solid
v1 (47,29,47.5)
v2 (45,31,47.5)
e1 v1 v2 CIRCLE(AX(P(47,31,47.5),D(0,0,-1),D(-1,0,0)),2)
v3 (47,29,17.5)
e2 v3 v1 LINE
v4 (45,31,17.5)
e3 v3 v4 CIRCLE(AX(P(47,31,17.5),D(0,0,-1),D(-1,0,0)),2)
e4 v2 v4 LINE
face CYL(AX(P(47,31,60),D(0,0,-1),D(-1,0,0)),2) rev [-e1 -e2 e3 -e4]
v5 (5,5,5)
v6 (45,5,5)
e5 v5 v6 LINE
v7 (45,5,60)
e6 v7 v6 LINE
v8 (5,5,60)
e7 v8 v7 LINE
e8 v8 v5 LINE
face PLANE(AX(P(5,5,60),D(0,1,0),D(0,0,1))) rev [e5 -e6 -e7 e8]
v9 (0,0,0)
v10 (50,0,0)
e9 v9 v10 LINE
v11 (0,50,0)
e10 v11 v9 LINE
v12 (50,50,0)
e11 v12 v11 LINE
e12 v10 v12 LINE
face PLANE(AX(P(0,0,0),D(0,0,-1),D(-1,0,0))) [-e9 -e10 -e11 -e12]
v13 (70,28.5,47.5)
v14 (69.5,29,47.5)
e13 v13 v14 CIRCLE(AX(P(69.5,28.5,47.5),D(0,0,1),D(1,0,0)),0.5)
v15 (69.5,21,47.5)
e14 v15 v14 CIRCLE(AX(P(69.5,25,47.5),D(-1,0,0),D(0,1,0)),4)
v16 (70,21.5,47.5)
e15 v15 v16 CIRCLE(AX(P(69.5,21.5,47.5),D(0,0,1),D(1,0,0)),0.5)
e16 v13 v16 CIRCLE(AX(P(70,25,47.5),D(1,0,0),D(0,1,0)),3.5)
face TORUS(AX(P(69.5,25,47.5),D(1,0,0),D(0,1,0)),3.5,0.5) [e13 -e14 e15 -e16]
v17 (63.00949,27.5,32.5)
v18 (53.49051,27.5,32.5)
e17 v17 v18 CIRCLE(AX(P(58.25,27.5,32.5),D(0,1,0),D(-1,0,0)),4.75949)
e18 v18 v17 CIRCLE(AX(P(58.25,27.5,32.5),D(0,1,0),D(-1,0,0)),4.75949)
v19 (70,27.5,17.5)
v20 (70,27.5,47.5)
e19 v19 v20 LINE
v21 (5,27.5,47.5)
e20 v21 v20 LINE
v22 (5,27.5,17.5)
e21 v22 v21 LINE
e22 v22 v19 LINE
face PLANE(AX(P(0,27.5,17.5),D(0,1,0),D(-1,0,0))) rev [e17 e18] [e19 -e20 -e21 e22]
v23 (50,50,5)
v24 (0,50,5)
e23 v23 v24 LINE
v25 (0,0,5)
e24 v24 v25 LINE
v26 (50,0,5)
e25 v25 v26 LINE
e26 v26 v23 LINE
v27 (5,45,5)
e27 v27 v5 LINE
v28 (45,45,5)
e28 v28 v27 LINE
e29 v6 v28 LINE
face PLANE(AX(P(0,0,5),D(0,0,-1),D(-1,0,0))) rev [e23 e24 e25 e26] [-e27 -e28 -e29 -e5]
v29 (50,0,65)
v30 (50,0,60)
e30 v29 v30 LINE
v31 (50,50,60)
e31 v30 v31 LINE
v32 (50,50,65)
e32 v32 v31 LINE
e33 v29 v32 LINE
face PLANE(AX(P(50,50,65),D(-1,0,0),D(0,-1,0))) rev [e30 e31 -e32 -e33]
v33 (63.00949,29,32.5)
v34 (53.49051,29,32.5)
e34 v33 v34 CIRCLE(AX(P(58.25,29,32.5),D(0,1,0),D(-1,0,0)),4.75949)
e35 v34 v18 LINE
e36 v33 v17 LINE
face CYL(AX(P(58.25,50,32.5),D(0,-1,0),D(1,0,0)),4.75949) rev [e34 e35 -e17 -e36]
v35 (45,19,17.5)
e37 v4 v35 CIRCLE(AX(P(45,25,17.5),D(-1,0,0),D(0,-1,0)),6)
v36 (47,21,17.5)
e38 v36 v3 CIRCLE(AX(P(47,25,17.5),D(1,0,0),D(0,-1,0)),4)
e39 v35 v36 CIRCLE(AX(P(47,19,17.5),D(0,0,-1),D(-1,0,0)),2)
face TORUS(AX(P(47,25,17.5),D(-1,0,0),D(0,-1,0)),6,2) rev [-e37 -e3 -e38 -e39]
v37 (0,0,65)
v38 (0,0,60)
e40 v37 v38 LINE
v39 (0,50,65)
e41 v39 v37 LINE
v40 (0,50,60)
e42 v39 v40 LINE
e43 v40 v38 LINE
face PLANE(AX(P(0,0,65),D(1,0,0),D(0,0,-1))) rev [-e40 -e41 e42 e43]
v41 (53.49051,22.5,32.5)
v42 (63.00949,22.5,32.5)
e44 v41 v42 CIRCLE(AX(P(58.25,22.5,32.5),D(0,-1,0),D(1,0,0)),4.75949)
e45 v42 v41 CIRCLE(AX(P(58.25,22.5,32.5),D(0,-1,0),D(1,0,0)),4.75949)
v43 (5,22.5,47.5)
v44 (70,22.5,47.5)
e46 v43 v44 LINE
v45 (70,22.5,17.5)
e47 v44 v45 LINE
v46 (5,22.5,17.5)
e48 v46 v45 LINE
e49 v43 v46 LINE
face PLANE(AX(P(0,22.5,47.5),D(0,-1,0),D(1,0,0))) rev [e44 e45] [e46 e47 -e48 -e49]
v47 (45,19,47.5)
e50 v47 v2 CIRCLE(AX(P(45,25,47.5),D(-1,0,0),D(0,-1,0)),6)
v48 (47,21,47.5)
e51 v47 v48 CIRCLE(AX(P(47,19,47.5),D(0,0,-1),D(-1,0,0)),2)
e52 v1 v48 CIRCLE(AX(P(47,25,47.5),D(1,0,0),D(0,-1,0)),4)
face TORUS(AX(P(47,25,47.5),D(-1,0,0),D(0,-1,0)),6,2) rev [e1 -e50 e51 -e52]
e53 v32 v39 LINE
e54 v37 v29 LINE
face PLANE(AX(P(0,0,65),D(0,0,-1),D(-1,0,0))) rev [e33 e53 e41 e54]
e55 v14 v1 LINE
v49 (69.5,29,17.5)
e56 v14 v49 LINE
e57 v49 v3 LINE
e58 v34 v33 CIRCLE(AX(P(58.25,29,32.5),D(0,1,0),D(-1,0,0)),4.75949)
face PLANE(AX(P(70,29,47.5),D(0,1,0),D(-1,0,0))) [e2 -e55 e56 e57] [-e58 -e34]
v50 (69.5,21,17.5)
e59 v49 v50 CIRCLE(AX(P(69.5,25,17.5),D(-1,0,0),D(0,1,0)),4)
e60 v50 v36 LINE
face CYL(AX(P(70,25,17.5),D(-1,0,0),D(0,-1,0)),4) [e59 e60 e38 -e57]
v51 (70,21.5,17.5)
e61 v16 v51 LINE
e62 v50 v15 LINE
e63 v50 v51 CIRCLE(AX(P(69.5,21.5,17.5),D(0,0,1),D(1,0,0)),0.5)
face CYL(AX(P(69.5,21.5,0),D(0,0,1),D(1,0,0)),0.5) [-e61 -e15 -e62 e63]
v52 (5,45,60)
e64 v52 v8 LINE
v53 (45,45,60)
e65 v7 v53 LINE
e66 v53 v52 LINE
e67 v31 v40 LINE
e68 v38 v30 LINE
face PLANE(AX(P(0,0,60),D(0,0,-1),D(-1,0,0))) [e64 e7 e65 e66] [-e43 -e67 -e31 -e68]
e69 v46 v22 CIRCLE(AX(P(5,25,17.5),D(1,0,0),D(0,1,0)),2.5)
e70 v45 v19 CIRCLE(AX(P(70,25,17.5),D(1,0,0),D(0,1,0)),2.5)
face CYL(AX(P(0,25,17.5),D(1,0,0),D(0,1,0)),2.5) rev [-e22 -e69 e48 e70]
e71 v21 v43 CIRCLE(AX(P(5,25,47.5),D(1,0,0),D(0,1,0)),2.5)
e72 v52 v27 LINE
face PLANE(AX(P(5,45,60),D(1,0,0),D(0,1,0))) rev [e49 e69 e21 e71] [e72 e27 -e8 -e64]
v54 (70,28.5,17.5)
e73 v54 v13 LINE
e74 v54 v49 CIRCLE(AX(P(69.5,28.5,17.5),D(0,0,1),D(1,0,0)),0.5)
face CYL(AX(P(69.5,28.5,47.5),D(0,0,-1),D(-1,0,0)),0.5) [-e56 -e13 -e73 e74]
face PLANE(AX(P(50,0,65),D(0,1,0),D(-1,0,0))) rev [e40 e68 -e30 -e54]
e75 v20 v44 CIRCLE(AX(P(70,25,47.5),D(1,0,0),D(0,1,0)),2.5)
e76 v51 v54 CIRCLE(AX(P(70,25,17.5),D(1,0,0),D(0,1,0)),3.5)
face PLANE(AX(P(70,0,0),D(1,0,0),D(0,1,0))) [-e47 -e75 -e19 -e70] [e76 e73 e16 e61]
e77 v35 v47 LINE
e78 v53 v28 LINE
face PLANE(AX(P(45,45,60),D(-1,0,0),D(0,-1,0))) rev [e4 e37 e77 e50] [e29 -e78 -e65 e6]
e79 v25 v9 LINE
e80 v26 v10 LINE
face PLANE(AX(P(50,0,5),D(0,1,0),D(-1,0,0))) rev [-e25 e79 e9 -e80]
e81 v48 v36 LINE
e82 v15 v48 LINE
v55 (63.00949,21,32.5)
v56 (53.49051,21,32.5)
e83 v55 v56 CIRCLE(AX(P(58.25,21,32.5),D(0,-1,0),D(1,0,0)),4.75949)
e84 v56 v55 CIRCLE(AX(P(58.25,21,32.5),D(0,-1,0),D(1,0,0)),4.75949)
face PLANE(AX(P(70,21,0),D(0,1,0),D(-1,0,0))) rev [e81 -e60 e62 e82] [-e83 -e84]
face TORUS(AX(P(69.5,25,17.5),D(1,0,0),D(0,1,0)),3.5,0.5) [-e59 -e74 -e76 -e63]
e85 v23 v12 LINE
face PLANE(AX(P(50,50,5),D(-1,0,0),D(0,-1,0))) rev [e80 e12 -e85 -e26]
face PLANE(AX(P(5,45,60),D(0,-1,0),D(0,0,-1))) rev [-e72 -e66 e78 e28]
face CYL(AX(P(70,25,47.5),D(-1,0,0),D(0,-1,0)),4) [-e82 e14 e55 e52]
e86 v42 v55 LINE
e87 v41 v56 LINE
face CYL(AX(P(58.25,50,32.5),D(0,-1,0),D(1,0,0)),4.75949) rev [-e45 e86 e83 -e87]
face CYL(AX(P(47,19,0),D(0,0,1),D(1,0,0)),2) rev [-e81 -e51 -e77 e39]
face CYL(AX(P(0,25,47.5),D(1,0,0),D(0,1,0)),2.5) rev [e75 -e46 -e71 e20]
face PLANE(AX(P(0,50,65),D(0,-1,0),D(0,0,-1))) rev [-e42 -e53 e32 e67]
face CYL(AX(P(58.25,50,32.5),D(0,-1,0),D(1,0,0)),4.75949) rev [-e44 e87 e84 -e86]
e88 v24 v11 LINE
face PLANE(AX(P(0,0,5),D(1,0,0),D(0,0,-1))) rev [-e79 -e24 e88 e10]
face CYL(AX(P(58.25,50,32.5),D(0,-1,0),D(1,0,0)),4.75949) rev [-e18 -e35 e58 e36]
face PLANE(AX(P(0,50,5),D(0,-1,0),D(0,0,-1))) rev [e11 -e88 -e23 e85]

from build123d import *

# Parameters (mm, degrees)
FRONT_FLANGE_SKETCH_W      = 50
FRONT_FLANGE_SKETCH_H      = 50
FRONT_FLANGE_50X50X5_DEPTH = 5
BODY_BLOCK_SKETCH_W        = 40
BODY_BLOCK_SKETCH_H        = 40
BODY_BLOCK_40X40X55_DEPTH  = 55
REAR_FLANGE_SKETCH_W       = 50
REAR_FLANGE_SKETCH_H       = 50
REAR_FLANGE_5MM_DEPTH      = 5
OBROUND_TONGUE_DEPTH       = 25
TONGUE_SLOT_CUT_DEPTH      = 108.819293264
TONGUE_ROOT_FILLET_R2_R    = 2
TONGUE_EDGE_FILLET_R0_5_R  = 0.5
TONGUE_HOLE_SKETCH_R       = 4.75949031
TONGUE_CROSS_HOLE_DEPTH    = 100.829855254


with BuildPart() as part:
    # Front Flange Sketch → Front Flange 50x50x5 (new body)
    with BuildSketch(Plane.XY):
        with Locations((25, 25)):
            Rectangle(FRONT_FLANGE_SKETCH_W, FRONT_FLANGE_SKETCH_H)
    extrude(amount=FRONT_FLANGE_50X50X5_DEPTH)

    # Body Block Sketch → Body Block 40x40x55 (add)
    with BuildSketch(Plane.XY.offset(5)):
        with Locations((25, 25)):
            Rectangle(BODY_BLOCK_SKETCH_W, BODY_BLOCK_SKETCH_H)
    extrude(amount=BODY_BLOCK_40X40X55_DEPTH)

    # Rear Flange Sketch → Rear Flange 5mm (add)
    with BuildSketch(Plane.XY.offset(60)):
        with Locations((25, 25)):
            Rectangle(REAR_FLANGE_SKETCH_W, REAR_FLANGE_SKETCH_H)
    extrude(amount=REAR_FLANGE_5MM_DEPTH)

    # Tongue Profile Sketch → Obround Tongue (add)
    with BuildSketch(Plane(origin=(45, 0, 0), x_dir=(0, 0, -1), z_dir=(1, 0, 0))):
        with BuildLine():
            Line((-47.5, 29), (-17.5, 29))
            ThreePointArc((-17.5, 29), (-13.5, 25), (-17.5, 21))
            Line((-17.5, 21), (-47.5, 21))
            ThreePointArc((-47.5, 21), (-51.5, 25), (-47.5, 29))
        make_face()
    extrude(amount=OBROUND_TONGUE_DEPTH)

    # Tongue Slot Sketch → Tongue Slot Cut (cut, through all)
    with BuildSketch(Plane(origin=(70, 0, 0), x_dir=(0, 0, -1), z_dir=(1, 0, 0))):
        with BuildLine():
            Line((-47.5, 22.5), (-17.5, 22.5))
            ThreePointArc((-17.5, 22.5), (-15, 25), (-17.5, 27.5))
            Line((-17.5, 27.5), (-47.5, 27.5))
            ThreePointArc((-47.5, 27.5), (-50, 25), (-47.5, 22.5))
        make_face()
    extrude(amount=-TONGUE_SLOT_CUT_DEPTH, mode=Mode.SUBTRACT)

    # Tongue Root Fillet R2
    tongue_root_fillet_r2_edges = [part.edges().sort_by_distance(p)[0] for p in [
        (45, 29, 32.5),
        (45, 25, 13.5),
        (45, 21, 32.5),
        (45, 25, 51.5),
    ]]
    fillet(tongue_root_fillet_r2_edges, radius=TONGUE_ROOT_FILLET_R2_R)

    # Tongue Edge Fillet R0.5
    tongue_edge_fillet_r0_5_edges = [part.edges().sort_by_distance(p)[0] for p in [
        (70, 21, 32.5),
        (70, 25, 13.5),
        (70, 25, 51.5),
        (70, 29, 32.5),
    ]]
    fillet(tongue_edge_fillet_r0_5_edges, radius=TONGUE_EDGE_FILLET_R0_5_R)

    # Tongue Hole Sketch → Tongue Cross Hole (cut, through all)
    with BuildSketch(Plane.XZ.offset(-21)):
        with Locations((58.25, 32.5)):
            Circle(TONGUE_HOLE_SKETCH_R)
    extrude(amount=-TONGUE_CROSS_HOLE_DEPTH, mode=Mode.SUBTRACT)


solid = part.part
